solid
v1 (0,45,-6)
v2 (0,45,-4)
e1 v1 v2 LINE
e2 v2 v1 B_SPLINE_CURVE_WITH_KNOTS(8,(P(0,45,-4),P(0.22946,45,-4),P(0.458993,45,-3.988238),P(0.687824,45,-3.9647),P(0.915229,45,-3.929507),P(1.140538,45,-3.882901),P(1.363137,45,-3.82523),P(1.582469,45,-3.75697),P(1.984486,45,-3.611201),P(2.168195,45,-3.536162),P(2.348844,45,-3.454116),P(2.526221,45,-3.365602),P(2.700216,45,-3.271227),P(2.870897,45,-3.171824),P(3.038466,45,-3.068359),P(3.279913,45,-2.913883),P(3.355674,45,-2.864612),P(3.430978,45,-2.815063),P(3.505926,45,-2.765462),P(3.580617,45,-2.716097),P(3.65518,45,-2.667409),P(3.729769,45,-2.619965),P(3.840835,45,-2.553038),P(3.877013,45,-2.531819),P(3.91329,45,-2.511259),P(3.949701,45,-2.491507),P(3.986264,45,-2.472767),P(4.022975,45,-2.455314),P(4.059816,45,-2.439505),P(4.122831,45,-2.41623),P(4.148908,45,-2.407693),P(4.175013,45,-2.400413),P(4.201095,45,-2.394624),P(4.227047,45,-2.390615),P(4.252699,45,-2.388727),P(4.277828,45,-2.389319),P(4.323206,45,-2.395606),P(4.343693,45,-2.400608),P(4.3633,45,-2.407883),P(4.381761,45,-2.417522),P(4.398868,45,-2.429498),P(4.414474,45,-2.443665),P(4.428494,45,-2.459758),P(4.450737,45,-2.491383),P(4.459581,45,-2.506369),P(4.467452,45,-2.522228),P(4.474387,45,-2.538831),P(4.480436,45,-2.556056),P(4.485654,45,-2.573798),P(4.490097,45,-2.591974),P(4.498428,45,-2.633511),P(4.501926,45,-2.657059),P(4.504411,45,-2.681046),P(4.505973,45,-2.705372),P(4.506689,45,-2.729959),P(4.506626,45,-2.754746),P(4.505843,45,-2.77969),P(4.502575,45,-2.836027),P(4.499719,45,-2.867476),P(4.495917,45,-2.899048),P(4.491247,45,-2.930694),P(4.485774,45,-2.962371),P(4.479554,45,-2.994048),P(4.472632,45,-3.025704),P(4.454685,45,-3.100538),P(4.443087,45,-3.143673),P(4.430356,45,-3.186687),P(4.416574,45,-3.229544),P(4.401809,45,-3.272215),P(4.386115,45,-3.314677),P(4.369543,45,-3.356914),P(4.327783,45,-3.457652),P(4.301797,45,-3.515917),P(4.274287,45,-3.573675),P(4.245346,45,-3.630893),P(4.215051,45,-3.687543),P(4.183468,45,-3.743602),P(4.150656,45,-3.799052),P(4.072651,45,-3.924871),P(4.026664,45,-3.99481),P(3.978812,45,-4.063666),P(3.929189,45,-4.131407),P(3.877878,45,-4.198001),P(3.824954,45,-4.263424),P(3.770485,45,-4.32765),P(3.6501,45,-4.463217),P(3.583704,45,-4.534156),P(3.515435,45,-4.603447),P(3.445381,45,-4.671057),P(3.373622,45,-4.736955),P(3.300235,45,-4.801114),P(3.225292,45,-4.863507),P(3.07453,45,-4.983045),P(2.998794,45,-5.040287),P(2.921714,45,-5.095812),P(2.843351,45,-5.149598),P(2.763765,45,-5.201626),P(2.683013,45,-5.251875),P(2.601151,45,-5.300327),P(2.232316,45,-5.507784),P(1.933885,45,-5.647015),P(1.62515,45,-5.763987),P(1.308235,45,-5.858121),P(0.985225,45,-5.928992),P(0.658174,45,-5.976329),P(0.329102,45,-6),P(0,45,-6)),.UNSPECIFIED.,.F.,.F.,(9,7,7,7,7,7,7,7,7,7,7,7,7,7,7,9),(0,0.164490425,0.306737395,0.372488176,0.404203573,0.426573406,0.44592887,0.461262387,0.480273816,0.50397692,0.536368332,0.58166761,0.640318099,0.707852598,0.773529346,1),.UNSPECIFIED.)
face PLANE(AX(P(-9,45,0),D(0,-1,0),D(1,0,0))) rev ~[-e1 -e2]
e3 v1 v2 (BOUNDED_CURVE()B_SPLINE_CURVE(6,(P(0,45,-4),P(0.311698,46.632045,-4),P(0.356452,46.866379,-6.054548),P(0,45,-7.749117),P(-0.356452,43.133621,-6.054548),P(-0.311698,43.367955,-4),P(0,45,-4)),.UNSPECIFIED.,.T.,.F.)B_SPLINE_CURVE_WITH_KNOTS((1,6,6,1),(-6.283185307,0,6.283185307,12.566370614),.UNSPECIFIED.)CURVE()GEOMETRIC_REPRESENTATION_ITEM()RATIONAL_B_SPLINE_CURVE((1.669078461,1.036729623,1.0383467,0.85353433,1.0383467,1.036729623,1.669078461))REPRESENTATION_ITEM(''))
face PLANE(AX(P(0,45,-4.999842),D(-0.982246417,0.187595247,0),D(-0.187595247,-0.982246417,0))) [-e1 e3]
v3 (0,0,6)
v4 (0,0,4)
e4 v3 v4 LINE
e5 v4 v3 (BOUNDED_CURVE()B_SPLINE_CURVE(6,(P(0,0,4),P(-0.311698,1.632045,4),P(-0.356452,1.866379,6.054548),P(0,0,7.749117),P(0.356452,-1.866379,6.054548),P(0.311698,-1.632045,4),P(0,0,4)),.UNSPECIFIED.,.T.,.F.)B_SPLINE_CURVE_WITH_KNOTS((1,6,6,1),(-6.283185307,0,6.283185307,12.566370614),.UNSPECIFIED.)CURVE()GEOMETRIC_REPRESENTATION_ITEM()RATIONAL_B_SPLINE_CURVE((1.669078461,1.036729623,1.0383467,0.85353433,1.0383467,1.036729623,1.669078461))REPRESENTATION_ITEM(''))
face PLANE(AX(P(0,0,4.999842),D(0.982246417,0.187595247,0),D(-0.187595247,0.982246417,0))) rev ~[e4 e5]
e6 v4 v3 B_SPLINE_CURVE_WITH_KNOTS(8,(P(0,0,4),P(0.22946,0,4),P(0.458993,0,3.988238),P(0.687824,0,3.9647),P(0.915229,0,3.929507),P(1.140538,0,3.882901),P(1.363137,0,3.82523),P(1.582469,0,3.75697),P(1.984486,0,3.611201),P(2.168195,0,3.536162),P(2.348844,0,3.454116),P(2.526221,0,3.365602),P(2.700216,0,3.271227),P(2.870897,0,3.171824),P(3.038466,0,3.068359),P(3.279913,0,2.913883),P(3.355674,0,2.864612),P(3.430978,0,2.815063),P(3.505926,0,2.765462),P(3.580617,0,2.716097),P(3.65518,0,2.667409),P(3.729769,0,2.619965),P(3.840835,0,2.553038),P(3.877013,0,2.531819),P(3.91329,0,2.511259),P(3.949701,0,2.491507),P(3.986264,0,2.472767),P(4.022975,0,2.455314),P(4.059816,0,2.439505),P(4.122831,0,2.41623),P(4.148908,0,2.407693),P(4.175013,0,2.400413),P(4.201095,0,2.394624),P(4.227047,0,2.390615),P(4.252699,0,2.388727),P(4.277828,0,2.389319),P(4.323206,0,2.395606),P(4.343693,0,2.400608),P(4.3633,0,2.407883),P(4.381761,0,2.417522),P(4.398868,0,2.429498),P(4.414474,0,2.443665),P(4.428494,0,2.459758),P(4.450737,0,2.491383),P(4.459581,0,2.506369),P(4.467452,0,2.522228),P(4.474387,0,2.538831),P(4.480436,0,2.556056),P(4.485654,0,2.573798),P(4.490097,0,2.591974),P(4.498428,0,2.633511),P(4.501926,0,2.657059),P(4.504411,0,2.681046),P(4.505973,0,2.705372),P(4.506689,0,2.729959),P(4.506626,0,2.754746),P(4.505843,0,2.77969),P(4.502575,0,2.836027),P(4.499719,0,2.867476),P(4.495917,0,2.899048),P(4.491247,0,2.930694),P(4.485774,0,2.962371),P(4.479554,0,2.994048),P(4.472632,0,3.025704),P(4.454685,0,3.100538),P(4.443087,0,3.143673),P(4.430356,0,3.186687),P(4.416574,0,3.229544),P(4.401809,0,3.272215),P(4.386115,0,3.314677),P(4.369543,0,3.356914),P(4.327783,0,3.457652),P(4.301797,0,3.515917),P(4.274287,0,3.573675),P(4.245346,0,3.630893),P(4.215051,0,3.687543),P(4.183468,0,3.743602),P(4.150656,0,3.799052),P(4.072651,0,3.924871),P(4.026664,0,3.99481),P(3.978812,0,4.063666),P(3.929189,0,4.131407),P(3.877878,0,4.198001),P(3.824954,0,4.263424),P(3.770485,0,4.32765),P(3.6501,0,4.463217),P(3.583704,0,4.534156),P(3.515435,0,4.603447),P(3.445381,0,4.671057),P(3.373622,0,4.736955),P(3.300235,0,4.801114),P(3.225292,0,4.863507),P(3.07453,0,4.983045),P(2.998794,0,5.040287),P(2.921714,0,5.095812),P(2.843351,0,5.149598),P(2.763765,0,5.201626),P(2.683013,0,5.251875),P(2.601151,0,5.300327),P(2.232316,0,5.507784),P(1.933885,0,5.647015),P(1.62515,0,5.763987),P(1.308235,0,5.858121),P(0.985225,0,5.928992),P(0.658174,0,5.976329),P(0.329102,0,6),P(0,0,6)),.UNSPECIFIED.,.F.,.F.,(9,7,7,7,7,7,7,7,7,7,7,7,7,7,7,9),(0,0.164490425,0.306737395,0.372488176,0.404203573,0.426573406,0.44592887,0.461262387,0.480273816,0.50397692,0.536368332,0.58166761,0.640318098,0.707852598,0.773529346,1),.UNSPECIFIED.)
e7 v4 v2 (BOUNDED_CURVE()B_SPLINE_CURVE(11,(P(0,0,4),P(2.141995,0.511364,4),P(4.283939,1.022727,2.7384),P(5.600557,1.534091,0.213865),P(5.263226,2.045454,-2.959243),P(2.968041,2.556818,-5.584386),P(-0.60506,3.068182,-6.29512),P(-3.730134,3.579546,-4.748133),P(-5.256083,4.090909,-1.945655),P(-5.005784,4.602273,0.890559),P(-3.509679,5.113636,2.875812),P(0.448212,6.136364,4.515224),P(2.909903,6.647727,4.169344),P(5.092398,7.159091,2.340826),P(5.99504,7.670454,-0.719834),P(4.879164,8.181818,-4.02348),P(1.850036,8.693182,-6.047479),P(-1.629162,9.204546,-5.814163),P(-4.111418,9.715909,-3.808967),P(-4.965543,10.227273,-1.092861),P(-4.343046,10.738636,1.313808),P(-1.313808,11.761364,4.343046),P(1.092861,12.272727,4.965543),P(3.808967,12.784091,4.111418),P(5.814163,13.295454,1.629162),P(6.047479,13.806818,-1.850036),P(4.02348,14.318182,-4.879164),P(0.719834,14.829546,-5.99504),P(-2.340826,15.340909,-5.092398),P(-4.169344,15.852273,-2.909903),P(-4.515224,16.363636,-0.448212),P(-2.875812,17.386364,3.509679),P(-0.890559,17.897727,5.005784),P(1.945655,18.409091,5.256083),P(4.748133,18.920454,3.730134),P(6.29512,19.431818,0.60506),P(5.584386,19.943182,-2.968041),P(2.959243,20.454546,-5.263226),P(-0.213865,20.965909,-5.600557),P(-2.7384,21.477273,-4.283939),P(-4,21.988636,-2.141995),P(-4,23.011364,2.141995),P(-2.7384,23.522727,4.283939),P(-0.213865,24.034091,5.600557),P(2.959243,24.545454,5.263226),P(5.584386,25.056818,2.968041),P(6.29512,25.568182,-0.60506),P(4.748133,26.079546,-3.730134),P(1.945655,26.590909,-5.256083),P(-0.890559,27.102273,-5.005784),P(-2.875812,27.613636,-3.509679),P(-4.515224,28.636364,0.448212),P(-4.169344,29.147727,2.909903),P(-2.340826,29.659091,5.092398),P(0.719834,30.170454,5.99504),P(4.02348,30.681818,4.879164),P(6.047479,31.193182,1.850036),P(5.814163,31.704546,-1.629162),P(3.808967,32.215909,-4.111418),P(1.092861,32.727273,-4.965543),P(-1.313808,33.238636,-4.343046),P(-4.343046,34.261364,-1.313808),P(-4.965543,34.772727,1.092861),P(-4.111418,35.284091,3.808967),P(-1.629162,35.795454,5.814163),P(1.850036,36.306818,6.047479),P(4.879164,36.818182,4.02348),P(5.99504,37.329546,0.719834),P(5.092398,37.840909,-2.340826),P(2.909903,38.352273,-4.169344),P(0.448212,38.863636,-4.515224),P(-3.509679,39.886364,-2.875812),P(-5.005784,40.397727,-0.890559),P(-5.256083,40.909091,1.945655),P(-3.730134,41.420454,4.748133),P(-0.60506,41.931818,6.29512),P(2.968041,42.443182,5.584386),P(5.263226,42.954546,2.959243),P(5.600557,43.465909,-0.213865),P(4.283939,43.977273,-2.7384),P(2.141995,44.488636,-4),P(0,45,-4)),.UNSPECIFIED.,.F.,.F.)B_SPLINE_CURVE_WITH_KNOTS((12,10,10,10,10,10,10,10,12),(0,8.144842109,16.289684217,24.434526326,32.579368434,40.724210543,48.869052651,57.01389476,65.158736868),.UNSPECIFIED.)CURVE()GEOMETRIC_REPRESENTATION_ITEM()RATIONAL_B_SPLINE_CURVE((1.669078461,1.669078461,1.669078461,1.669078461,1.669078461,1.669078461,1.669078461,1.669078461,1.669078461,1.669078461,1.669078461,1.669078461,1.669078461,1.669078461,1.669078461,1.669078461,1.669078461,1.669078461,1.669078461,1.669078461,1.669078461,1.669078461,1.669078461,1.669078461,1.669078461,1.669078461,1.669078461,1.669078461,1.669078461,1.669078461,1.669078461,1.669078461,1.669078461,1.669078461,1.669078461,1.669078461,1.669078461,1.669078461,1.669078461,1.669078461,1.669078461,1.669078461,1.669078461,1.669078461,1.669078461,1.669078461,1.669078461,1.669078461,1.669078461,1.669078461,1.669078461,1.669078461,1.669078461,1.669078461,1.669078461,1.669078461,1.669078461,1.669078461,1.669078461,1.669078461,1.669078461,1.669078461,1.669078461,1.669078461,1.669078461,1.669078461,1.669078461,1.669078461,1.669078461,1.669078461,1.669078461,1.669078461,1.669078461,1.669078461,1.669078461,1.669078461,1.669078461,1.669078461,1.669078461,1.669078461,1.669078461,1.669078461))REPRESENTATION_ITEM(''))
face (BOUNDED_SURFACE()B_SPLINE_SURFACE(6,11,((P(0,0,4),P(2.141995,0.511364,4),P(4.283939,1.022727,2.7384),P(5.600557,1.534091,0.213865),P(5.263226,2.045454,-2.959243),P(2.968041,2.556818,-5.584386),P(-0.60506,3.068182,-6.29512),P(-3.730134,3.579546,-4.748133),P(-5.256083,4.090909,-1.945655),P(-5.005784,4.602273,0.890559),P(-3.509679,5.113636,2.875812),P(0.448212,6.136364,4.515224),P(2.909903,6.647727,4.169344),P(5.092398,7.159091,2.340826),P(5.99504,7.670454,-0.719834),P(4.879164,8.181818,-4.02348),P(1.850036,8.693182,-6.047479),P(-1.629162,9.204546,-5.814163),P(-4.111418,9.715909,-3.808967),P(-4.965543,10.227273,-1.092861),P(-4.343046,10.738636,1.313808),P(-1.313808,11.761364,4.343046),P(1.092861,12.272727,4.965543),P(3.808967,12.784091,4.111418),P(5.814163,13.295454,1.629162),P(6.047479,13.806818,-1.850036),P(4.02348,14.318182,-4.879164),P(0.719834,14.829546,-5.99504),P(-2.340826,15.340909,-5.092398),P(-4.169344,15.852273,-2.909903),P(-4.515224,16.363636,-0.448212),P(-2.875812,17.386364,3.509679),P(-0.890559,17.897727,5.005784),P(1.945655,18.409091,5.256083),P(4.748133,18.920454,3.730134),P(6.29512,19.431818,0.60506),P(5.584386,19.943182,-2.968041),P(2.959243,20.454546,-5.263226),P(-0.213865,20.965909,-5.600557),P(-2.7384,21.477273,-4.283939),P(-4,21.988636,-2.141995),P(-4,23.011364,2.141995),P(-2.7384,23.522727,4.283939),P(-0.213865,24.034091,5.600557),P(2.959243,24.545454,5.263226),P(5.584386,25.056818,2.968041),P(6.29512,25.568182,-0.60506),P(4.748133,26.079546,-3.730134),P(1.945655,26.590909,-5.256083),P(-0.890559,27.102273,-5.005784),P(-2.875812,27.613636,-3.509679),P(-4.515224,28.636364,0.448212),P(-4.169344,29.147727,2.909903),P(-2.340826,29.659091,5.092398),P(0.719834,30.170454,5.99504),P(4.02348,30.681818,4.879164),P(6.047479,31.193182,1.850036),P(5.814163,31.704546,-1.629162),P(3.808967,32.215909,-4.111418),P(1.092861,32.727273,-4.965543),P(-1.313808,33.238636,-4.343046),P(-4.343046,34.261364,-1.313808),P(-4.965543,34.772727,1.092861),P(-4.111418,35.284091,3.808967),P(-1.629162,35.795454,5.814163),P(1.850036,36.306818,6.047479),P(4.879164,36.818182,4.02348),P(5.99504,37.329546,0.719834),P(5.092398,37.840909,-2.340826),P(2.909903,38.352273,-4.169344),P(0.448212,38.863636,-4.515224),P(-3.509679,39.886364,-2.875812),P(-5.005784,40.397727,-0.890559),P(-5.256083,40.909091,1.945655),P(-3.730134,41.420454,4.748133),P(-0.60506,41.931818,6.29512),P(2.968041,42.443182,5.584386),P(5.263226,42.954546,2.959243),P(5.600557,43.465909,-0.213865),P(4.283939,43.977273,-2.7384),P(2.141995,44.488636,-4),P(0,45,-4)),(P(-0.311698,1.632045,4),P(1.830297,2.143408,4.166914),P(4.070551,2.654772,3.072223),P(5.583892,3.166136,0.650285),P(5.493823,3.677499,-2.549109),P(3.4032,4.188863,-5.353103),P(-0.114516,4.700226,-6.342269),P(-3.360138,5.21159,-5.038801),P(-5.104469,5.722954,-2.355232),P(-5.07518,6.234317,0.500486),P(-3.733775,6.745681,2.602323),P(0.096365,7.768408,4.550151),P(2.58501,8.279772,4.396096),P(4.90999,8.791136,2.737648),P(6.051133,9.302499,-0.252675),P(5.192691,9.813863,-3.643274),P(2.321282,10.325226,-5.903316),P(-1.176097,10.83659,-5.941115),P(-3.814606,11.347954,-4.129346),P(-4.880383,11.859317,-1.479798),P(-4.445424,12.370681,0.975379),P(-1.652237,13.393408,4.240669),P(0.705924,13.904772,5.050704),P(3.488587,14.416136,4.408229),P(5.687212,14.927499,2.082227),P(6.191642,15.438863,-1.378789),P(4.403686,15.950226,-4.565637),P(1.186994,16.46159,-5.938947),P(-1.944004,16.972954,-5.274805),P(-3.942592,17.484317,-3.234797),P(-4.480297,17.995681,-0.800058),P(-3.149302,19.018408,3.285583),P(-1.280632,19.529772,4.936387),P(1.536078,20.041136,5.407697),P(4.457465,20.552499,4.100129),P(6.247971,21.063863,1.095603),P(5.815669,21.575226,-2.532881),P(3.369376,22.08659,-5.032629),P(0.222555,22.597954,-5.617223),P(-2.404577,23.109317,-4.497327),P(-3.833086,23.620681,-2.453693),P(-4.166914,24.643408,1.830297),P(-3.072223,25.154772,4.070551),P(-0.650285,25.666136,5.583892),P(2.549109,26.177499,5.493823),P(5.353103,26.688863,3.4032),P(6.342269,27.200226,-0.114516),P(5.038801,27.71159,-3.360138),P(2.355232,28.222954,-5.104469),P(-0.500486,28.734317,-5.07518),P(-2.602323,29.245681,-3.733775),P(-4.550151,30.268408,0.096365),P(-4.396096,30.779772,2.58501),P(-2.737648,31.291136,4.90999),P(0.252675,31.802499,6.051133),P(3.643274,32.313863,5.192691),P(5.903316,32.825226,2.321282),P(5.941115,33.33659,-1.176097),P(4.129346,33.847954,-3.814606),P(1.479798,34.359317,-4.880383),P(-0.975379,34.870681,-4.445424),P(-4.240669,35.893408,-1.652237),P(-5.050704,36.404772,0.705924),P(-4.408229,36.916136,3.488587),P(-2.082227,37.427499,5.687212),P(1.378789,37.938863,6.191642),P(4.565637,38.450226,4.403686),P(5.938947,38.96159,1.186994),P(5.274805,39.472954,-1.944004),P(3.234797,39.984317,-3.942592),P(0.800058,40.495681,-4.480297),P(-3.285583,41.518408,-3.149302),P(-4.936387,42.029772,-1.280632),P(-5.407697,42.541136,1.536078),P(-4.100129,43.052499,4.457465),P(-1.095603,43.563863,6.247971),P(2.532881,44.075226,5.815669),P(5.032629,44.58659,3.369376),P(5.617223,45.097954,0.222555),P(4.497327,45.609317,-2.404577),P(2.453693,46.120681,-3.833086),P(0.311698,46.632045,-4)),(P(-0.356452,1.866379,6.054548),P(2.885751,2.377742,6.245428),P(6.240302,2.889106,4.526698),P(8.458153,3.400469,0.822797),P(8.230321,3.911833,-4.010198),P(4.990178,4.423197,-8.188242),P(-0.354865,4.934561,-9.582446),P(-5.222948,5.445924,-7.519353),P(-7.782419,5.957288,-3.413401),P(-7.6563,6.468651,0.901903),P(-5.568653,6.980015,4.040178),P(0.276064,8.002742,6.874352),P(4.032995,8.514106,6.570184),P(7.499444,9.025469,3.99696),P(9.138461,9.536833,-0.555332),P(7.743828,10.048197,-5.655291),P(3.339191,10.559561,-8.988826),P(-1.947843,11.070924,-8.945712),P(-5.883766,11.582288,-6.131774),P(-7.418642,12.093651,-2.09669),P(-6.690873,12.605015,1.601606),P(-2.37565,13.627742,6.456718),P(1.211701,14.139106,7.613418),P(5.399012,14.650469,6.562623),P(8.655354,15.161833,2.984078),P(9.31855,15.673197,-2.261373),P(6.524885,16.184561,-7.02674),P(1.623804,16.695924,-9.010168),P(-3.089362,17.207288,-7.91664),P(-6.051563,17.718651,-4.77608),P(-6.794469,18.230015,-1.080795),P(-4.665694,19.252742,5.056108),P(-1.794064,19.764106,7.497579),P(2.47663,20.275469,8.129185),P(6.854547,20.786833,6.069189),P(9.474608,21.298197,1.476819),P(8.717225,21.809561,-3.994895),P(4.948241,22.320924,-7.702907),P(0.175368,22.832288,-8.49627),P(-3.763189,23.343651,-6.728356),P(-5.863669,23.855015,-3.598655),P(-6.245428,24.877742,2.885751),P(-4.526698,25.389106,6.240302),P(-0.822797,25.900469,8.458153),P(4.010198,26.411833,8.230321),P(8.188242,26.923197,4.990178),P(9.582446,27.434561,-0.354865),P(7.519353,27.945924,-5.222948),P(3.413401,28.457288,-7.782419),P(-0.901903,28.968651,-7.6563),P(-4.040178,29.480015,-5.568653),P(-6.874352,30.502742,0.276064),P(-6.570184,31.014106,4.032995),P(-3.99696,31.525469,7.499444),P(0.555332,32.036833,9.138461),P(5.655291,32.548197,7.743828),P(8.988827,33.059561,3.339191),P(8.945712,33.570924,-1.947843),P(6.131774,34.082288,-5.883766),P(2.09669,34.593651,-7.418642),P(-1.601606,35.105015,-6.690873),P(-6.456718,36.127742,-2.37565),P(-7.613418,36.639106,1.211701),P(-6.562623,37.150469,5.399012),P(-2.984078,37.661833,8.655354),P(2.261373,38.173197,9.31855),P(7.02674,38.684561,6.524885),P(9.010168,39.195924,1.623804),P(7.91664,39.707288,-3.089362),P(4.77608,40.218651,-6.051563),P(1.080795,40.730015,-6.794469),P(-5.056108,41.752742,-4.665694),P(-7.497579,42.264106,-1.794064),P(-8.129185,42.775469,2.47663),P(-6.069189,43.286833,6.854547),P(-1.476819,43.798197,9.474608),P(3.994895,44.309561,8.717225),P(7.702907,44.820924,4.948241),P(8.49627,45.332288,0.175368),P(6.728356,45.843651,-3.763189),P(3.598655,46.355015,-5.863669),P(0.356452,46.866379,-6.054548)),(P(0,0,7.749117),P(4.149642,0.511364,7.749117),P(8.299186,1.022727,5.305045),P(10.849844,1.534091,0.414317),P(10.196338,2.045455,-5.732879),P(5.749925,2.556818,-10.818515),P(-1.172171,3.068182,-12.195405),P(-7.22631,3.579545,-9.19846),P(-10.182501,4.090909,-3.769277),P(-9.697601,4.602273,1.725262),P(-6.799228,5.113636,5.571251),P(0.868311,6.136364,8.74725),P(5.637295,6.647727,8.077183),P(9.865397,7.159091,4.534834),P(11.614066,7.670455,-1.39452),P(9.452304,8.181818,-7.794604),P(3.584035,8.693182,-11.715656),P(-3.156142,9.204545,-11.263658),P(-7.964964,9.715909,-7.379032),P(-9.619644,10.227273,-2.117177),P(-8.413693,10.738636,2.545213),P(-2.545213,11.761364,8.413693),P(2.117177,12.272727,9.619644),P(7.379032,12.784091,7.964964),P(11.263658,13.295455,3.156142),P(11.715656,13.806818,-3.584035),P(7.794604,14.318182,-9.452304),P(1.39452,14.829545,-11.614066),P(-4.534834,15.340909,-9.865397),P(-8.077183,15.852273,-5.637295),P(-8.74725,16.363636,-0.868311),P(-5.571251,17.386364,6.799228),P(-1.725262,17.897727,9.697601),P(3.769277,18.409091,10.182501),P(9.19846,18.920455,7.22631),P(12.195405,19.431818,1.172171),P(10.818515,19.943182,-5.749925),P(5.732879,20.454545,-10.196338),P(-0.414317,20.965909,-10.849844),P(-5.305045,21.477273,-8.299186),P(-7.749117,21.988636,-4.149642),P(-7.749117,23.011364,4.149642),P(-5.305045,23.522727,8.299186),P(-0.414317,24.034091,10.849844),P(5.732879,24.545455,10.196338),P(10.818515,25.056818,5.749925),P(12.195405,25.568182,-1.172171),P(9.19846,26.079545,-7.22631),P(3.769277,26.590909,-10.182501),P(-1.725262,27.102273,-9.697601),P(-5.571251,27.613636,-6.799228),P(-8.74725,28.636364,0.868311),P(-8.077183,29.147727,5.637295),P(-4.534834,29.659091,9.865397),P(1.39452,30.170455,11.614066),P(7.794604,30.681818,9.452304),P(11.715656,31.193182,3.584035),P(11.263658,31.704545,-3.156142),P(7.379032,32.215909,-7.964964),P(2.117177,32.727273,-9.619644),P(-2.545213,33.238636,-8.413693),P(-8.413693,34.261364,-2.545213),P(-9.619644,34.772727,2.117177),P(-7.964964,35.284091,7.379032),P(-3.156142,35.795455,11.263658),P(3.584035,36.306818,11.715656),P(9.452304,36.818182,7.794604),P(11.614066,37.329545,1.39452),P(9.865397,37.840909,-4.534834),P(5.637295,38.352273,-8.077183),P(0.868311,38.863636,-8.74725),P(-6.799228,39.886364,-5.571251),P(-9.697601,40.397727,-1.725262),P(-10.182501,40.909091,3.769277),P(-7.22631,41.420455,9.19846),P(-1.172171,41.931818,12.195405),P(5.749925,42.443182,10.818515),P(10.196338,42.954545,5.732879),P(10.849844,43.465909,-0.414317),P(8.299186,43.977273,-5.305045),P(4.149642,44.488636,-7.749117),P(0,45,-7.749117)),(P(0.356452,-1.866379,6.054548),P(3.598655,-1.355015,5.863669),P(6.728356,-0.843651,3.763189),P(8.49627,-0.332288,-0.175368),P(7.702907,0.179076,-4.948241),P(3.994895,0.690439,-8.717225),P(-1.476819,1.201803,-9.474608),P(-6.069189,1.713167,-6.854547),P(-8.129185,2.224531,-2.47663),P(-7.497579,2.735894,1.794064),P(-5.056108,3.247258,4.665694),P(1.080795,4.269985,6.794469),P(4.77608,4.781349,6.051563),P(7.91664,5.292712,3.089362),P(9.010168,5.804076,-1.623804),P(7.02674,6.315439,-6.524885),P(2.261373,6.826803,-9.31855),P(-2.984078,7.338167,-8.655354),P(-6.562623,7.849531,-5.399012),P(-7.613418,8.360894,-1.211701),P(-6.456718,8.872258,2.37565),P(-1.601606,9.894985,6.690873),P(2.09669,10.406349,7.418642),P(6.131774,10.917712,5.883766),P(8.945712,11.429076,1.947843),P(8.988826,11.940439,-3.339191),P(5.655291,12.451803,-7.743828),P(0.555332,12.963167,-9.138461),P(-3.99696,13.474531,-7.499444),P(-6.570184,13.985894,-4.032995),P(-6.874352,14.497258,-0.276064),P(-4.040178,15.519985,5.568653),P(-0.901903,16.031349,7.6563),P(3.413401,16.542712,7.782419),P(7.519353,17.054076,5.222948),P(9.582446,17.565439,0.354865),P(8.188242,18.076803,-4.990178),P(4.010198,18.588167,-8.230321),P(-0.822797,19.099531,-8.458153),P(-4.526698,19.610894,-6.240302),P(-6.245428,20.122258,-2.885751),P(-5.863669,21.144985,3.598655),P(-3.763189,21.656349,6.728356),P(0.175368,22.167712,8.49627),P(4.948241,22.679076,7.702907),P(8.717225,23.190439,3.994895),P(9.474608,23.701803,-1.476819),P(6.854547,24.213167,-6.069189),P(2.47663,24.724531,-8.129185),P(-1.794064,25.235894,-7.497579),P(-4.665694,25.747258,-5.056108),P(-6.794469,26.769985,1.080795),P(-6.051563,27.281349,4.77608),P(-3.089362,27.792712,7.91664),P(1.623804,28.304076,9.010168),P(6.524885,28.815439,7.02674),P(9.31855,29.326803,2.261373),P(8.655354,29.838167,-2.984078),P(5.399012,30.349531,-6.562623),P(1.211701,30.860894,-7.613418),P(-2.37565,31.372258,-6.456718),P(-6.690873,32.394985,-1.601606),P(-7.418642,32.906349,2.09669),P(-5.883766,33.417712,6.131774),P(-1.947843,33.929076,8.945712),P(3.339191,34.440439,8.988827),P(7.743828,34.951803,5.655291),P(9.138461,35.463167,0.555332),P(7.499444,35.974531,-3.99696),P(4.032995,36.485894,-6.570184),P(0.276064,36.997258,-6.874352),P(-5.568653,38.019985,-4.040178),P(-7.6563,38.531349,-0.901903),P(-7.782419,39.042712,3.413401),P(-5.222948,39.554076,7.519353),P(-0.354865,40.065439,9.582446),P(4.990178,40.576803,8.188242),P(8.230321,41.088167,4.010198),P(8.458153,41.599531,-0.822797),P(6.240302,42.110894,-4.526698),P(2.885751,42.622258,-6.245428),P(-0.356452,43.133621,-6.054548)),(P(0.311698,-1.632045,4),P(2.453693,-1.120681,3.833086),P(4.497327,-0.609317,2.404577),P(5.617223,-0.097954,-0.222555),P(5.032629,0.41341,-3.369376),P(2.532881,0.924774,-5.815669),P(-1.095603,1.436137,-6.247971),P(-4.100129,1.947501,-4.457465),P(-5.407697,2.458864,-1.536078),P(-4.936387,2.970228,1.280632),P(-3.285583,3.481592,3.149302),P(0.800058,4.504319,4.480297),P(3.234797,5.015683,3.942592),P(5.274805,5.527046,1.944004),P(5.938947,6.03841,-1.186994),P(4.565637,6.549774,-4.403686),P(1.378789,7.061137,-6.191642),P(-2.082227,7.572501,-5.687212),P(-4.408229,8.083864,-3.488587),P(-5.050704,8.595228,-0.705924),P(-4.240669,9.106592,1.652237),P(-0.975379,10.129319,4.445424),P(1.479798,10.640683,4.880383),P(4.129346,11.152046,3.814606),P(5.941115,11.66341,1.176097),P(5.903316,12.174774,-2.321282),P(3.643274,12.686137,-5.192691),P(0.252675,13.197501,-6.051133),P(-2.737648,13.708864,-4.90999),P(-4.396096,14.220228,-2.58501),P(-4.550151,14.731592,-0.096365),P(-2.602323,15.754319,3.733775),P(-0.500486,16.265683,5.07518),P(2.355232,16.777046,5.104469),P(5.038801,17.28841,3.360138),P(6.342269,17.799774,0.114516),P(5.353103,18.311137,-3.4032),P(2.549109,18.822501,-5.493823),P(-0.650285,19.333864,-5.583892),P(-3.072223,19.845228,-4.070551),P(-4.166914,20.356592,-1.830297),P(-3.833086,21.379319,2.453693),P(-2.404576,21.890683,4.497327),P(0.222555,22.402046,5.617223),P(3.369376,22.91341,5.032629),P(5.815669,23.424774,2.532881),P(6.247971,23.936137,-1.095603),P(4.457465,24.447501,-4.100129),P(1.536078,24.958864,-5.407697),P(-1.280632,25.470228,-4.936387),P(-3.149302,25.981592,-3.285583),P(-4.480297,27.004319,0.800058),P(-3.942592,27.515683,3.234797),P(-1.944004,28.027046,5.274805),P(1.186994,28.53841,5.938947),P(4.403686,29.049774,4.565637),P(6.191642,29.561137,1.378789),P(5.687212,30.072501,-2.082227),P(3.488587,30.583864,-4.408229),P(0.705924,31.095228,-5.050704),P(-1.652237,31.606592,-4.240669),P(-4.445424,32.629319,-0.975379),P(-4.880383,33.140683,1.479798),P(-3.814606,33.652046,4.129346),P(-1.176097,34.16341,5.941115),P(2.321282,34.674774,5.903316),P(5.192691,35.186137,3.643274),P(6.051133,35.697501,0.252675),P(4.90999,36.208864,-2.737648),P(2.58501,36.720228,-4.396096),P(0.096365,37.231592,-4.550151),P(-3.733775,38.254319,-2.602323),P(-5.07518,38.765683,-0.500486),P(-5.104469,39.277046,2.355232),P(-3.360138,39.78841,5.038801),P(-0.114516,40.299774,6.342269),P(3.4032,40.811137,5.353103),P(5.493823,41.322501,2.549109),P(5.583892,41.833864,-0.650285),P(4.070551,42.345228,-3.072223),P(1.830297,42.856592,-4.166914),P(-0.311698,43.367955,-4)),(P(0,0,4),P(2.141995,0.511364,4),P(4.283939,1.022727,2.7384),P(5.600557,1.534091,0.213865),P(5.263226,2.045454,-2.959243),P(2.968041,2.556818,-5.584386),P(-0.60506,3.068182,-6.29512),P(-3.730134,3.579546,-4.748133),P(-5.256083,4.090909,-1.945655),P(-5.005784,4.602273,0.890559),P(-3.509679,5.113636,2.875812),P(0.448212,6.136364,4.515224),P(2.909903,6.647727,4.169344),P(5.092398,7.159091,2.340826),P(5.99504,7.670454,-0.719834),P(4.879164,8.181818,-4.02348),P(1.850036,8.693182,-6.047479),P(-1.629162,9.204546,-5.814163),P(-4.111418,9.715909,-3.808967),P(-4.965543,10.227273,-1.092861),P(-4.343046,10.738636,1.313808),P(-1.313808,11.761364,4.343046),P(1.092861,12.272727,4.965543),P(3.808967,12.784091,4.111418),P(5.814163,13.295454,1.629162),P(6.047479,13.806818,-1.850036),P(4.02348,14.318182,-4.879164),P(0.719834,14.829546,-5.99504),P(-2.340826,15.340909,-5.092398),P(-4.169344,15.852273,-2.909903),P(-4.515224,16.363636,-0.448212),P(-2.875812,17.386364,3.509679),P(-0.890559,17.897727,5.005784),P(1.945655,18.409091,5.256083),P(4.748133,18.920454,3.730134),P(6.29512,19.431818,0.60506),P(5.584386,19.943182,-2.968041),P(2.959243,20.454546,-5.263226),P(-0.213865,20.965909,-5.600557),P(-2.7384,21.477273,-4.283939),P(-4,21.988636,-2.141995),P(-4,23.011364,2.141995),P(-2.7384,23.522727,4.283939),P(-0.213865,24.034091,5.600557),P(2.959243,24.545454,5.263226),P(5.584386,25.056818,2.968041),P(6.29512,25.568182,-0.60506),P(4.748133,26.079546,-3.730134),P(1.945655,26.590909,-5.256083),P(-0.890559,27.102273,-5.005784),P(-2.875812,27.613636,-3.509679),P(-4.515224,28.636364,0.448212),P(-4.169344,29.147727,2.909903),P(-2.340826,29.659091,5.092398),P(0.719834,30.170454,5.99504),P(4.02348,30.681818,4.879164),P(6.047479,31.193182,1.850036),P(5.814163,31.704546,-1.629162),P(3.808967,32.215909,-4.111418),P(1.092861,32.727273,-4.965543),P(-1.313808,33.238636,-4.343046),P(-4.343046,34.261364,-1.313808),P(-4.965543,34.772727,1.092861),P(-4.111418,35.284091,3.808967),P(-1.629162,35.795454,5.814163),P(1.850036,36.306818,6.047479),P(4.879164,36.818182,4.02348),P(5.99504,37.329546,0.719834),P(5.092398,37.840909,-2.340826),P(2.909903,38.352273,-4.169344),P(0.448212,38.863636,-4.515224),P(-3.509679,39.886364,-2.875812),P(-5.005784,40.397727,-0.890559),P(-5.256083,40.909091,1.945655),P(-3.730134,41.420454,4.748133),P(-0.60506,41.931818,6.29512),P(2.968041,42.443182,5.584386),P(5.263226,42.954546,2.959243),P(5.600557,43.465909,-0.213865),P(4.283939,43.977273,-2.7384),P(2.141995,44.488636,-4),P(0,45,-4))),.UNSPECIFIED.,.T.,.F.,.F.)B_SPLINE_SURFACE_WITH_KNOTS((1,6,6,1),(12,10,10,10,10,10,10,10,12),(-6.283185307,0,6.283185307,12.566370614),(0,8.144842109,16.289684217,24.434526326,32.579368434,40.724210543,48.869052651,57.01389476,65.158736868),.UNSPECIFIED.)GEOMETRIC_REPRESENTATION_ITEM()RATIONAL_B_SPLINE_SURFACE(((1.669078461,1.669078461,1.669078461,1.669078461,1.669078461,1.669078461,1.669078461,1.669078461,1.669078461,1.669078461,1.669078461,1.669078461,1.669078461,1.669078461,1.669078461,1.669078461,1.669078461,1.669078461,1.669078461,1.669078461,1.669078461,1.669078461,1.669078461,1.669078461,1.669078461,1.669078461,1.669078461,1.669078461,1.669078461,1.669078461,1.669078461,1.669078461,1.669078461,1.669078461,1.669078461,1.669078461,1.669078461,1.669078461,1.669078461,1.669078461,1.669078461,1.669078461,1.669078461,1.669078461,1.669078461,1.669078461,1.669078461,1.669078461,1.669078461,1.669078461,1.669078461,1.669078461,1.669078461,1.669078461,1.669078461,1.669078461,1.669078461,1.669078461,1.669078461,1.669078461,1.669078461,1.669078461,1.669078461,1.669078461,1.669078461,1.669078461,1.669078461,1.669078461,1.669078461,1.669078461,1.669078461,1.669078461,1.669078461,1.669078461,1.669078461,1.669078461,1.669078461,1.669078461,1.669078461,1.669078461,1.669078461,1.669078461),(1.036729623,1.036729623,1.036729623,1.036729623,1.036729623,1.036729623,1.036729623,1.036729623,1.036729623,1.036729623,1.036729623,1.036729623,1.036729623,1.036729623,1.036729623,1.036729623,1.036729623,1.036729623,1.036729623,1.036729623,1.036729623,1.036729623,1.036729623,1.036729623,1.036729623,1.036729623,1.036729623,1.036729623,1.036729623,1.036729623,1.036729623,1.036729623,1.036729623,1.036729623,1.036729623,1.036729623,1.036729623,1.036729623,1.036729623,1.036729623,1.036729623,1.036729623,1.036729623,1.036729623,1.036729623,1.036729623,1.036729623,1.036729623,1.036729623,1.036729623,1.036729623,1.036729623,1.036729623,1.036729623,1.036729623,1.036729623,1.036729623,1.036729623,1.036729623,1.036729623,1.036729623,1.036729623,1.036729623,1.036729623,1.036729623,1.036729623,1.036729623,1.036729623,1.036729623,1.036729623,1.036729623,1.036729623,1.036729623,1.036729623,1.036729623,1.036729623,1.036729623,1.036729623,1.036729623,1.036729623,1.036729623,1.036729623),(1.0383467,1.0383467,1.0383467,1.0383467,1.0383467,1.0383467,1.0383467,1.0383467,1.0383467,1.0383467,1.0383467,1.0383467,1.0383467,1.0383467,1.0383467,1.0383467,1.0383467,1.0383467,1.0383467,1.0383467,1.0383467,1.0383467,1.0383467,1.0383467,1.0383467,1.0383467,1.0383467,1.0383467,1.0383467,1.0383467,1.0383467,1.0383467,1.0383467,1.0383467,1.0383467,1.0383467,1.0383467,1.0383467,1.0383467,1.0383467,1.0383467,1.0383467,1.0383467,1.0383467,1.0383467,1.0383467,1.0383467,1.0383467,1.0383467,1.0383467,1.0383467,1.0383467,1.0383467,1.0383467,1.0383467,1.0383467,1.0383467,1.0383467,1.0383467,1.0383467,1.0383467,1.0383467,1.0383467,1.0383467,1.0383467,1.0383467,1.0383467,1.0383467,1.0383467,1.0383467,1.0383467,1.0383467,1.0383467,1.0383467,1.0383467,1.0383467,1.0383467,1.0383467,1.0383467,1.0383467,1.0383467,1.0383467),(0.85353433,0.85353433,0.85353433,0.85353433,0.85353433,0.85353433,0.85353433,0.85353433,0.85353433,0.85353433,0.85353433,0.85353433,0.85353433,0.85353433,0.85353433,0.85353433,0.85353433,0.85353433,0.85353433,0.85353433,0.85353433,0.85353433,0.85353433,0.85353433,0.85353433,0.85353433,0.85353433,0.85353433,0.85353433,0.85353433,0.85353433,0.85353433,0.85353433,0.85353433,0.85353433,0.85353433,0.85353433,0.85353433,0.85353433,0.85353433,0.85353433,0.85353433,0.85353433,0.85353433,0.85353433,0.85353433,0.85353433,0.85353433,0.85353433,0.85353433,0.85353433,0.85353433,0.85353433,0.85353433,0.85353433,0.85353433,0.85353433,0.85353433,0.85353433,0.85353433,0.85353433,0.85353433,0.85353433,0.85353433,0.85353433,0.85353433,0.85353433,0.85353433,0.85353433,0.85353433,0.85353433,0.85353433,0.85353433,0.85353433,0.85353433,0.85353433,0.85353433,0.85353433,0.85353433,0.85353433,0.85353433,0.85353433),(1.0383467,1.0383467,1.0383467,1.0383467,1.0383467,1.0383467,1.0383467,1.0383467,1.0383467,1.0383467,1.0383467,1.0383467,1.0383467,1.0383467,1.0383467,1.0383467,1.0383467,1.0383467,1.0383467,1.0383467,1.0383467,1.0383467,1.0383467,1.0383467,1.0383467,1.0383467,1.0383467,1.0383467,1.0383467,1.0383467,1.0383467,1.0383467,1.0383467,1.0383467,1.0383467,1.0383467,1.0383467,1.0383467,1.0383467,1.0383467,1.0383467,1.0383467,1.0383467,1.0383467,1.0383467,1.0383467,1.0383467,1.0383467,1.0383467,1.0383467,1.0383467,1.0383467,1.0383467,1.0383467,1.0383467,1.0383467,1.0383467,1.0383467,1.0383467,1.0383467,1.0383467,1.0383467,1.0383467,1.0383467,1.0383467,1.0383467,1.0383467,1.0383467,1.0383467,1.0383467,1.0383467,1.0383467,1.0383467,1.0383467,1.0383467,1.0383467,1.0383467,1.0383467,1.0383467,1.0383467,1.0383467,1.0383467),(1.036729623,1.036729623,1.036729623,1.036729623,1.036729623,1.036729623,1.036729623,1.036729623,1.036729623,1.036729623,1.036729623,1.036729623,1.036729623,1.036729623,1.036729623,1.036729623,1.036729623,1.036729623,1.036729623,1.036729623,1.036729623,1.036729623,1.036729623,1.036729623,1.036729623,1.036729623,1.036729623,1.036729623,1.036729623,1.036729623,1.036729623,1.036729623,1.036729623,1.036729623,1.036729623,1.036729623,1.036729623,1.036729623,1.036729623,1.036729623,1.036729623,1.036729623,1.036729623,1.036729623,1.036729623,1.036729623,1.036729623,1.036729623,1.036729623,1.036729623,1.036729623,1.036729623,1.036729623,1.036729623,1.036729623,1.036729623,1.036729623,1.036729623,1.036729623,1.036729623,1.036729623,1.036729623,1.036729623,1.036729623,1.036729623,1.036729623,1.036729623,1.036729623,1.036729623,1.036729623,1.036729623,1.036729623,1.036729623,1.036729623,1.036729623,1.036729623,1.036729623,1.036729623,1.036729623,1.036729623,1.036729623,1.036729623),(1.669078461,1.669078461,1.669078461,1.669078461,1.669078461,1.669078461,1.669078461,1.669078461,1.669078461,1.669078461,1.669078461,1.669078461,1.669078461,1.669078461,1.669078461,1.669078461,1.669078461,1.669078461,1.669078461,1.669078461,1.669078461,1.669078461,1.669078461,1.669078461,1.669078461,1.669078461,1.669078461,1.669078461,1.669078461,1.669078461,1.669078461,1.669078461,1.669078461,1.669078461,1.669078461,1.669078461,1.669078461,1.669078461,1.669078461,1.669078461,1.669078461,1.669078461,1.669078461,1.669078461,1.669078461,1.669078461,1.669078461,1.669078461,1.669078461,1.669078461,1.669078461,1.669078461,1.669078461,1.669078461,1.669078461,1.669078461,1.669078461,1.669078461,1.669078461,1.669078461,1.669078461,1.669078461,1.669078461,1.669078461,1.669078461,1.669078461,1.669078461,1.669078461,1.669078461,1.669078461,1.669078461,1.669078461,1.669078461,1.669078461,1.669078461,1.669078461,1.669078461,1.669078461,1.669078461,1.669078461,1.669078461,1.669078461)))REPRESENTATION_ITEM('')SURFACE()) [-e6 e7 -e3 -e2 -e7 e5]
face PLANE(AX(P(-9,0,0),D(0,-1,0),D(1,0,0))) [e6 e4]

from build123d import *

# Parameters (mm, degrees)
SWEEP2_PITCH        = 6
SWEEP2_HEIGHT       = 45
SWEEP2_RADIUS       = 5
SKETCH5_R           = 1
SKETCH6_OUTSIDE_W   = 23.988
SKETCH6_OUTSIDE_H   = 58.952
SKETCH6_OUTSIDE_W_2 = 18
SKETCH6_OUTSIDE_H_2 = 45
END_GROUND_DEPTH    = 9


with BuildPart() as part:
    # Sweep2: sweep along a helix
    with BuildLine() as sweep2_path:
        Helix(SWEEP2_PITCH, SWEEP2_HEIGHT, SWEEP2_RADIUS, center=(0, 0, 0), direction=(0, 1, 0))
    # Sketch5 → Sweep2 (sweep)
    with BuildSketch(Plane(origin=(0, 0, 5), x_dir=(0, 0, -1), z_dir=(0.9822464167783632, 0.1875952470774938, 0))):
        Circle(SKETCH5_R)
    sweep(path=sweep2_path.line, is_frenet=True)

    # Sketch6 outside → End Ground (cut, symmetric)
    with BuildSketch(Plane.XY):
        with Locations((0, 22.5)):
            Rectangle(SKETCH6_OUTSIDE_W, SKETCH6_OUTSIDE_H)
        with Locations((0, 22.5)):
            Rectangle(SKETCH6_OUTSIDE_W_2, SKETCH6_OUTSIDE_H_2, mode=Mode.SUBTRACT)
    extrude(amount=END_GROUND_DEPTH, both=True, mode=Mode.SUBTRACT)


solid = part.part
